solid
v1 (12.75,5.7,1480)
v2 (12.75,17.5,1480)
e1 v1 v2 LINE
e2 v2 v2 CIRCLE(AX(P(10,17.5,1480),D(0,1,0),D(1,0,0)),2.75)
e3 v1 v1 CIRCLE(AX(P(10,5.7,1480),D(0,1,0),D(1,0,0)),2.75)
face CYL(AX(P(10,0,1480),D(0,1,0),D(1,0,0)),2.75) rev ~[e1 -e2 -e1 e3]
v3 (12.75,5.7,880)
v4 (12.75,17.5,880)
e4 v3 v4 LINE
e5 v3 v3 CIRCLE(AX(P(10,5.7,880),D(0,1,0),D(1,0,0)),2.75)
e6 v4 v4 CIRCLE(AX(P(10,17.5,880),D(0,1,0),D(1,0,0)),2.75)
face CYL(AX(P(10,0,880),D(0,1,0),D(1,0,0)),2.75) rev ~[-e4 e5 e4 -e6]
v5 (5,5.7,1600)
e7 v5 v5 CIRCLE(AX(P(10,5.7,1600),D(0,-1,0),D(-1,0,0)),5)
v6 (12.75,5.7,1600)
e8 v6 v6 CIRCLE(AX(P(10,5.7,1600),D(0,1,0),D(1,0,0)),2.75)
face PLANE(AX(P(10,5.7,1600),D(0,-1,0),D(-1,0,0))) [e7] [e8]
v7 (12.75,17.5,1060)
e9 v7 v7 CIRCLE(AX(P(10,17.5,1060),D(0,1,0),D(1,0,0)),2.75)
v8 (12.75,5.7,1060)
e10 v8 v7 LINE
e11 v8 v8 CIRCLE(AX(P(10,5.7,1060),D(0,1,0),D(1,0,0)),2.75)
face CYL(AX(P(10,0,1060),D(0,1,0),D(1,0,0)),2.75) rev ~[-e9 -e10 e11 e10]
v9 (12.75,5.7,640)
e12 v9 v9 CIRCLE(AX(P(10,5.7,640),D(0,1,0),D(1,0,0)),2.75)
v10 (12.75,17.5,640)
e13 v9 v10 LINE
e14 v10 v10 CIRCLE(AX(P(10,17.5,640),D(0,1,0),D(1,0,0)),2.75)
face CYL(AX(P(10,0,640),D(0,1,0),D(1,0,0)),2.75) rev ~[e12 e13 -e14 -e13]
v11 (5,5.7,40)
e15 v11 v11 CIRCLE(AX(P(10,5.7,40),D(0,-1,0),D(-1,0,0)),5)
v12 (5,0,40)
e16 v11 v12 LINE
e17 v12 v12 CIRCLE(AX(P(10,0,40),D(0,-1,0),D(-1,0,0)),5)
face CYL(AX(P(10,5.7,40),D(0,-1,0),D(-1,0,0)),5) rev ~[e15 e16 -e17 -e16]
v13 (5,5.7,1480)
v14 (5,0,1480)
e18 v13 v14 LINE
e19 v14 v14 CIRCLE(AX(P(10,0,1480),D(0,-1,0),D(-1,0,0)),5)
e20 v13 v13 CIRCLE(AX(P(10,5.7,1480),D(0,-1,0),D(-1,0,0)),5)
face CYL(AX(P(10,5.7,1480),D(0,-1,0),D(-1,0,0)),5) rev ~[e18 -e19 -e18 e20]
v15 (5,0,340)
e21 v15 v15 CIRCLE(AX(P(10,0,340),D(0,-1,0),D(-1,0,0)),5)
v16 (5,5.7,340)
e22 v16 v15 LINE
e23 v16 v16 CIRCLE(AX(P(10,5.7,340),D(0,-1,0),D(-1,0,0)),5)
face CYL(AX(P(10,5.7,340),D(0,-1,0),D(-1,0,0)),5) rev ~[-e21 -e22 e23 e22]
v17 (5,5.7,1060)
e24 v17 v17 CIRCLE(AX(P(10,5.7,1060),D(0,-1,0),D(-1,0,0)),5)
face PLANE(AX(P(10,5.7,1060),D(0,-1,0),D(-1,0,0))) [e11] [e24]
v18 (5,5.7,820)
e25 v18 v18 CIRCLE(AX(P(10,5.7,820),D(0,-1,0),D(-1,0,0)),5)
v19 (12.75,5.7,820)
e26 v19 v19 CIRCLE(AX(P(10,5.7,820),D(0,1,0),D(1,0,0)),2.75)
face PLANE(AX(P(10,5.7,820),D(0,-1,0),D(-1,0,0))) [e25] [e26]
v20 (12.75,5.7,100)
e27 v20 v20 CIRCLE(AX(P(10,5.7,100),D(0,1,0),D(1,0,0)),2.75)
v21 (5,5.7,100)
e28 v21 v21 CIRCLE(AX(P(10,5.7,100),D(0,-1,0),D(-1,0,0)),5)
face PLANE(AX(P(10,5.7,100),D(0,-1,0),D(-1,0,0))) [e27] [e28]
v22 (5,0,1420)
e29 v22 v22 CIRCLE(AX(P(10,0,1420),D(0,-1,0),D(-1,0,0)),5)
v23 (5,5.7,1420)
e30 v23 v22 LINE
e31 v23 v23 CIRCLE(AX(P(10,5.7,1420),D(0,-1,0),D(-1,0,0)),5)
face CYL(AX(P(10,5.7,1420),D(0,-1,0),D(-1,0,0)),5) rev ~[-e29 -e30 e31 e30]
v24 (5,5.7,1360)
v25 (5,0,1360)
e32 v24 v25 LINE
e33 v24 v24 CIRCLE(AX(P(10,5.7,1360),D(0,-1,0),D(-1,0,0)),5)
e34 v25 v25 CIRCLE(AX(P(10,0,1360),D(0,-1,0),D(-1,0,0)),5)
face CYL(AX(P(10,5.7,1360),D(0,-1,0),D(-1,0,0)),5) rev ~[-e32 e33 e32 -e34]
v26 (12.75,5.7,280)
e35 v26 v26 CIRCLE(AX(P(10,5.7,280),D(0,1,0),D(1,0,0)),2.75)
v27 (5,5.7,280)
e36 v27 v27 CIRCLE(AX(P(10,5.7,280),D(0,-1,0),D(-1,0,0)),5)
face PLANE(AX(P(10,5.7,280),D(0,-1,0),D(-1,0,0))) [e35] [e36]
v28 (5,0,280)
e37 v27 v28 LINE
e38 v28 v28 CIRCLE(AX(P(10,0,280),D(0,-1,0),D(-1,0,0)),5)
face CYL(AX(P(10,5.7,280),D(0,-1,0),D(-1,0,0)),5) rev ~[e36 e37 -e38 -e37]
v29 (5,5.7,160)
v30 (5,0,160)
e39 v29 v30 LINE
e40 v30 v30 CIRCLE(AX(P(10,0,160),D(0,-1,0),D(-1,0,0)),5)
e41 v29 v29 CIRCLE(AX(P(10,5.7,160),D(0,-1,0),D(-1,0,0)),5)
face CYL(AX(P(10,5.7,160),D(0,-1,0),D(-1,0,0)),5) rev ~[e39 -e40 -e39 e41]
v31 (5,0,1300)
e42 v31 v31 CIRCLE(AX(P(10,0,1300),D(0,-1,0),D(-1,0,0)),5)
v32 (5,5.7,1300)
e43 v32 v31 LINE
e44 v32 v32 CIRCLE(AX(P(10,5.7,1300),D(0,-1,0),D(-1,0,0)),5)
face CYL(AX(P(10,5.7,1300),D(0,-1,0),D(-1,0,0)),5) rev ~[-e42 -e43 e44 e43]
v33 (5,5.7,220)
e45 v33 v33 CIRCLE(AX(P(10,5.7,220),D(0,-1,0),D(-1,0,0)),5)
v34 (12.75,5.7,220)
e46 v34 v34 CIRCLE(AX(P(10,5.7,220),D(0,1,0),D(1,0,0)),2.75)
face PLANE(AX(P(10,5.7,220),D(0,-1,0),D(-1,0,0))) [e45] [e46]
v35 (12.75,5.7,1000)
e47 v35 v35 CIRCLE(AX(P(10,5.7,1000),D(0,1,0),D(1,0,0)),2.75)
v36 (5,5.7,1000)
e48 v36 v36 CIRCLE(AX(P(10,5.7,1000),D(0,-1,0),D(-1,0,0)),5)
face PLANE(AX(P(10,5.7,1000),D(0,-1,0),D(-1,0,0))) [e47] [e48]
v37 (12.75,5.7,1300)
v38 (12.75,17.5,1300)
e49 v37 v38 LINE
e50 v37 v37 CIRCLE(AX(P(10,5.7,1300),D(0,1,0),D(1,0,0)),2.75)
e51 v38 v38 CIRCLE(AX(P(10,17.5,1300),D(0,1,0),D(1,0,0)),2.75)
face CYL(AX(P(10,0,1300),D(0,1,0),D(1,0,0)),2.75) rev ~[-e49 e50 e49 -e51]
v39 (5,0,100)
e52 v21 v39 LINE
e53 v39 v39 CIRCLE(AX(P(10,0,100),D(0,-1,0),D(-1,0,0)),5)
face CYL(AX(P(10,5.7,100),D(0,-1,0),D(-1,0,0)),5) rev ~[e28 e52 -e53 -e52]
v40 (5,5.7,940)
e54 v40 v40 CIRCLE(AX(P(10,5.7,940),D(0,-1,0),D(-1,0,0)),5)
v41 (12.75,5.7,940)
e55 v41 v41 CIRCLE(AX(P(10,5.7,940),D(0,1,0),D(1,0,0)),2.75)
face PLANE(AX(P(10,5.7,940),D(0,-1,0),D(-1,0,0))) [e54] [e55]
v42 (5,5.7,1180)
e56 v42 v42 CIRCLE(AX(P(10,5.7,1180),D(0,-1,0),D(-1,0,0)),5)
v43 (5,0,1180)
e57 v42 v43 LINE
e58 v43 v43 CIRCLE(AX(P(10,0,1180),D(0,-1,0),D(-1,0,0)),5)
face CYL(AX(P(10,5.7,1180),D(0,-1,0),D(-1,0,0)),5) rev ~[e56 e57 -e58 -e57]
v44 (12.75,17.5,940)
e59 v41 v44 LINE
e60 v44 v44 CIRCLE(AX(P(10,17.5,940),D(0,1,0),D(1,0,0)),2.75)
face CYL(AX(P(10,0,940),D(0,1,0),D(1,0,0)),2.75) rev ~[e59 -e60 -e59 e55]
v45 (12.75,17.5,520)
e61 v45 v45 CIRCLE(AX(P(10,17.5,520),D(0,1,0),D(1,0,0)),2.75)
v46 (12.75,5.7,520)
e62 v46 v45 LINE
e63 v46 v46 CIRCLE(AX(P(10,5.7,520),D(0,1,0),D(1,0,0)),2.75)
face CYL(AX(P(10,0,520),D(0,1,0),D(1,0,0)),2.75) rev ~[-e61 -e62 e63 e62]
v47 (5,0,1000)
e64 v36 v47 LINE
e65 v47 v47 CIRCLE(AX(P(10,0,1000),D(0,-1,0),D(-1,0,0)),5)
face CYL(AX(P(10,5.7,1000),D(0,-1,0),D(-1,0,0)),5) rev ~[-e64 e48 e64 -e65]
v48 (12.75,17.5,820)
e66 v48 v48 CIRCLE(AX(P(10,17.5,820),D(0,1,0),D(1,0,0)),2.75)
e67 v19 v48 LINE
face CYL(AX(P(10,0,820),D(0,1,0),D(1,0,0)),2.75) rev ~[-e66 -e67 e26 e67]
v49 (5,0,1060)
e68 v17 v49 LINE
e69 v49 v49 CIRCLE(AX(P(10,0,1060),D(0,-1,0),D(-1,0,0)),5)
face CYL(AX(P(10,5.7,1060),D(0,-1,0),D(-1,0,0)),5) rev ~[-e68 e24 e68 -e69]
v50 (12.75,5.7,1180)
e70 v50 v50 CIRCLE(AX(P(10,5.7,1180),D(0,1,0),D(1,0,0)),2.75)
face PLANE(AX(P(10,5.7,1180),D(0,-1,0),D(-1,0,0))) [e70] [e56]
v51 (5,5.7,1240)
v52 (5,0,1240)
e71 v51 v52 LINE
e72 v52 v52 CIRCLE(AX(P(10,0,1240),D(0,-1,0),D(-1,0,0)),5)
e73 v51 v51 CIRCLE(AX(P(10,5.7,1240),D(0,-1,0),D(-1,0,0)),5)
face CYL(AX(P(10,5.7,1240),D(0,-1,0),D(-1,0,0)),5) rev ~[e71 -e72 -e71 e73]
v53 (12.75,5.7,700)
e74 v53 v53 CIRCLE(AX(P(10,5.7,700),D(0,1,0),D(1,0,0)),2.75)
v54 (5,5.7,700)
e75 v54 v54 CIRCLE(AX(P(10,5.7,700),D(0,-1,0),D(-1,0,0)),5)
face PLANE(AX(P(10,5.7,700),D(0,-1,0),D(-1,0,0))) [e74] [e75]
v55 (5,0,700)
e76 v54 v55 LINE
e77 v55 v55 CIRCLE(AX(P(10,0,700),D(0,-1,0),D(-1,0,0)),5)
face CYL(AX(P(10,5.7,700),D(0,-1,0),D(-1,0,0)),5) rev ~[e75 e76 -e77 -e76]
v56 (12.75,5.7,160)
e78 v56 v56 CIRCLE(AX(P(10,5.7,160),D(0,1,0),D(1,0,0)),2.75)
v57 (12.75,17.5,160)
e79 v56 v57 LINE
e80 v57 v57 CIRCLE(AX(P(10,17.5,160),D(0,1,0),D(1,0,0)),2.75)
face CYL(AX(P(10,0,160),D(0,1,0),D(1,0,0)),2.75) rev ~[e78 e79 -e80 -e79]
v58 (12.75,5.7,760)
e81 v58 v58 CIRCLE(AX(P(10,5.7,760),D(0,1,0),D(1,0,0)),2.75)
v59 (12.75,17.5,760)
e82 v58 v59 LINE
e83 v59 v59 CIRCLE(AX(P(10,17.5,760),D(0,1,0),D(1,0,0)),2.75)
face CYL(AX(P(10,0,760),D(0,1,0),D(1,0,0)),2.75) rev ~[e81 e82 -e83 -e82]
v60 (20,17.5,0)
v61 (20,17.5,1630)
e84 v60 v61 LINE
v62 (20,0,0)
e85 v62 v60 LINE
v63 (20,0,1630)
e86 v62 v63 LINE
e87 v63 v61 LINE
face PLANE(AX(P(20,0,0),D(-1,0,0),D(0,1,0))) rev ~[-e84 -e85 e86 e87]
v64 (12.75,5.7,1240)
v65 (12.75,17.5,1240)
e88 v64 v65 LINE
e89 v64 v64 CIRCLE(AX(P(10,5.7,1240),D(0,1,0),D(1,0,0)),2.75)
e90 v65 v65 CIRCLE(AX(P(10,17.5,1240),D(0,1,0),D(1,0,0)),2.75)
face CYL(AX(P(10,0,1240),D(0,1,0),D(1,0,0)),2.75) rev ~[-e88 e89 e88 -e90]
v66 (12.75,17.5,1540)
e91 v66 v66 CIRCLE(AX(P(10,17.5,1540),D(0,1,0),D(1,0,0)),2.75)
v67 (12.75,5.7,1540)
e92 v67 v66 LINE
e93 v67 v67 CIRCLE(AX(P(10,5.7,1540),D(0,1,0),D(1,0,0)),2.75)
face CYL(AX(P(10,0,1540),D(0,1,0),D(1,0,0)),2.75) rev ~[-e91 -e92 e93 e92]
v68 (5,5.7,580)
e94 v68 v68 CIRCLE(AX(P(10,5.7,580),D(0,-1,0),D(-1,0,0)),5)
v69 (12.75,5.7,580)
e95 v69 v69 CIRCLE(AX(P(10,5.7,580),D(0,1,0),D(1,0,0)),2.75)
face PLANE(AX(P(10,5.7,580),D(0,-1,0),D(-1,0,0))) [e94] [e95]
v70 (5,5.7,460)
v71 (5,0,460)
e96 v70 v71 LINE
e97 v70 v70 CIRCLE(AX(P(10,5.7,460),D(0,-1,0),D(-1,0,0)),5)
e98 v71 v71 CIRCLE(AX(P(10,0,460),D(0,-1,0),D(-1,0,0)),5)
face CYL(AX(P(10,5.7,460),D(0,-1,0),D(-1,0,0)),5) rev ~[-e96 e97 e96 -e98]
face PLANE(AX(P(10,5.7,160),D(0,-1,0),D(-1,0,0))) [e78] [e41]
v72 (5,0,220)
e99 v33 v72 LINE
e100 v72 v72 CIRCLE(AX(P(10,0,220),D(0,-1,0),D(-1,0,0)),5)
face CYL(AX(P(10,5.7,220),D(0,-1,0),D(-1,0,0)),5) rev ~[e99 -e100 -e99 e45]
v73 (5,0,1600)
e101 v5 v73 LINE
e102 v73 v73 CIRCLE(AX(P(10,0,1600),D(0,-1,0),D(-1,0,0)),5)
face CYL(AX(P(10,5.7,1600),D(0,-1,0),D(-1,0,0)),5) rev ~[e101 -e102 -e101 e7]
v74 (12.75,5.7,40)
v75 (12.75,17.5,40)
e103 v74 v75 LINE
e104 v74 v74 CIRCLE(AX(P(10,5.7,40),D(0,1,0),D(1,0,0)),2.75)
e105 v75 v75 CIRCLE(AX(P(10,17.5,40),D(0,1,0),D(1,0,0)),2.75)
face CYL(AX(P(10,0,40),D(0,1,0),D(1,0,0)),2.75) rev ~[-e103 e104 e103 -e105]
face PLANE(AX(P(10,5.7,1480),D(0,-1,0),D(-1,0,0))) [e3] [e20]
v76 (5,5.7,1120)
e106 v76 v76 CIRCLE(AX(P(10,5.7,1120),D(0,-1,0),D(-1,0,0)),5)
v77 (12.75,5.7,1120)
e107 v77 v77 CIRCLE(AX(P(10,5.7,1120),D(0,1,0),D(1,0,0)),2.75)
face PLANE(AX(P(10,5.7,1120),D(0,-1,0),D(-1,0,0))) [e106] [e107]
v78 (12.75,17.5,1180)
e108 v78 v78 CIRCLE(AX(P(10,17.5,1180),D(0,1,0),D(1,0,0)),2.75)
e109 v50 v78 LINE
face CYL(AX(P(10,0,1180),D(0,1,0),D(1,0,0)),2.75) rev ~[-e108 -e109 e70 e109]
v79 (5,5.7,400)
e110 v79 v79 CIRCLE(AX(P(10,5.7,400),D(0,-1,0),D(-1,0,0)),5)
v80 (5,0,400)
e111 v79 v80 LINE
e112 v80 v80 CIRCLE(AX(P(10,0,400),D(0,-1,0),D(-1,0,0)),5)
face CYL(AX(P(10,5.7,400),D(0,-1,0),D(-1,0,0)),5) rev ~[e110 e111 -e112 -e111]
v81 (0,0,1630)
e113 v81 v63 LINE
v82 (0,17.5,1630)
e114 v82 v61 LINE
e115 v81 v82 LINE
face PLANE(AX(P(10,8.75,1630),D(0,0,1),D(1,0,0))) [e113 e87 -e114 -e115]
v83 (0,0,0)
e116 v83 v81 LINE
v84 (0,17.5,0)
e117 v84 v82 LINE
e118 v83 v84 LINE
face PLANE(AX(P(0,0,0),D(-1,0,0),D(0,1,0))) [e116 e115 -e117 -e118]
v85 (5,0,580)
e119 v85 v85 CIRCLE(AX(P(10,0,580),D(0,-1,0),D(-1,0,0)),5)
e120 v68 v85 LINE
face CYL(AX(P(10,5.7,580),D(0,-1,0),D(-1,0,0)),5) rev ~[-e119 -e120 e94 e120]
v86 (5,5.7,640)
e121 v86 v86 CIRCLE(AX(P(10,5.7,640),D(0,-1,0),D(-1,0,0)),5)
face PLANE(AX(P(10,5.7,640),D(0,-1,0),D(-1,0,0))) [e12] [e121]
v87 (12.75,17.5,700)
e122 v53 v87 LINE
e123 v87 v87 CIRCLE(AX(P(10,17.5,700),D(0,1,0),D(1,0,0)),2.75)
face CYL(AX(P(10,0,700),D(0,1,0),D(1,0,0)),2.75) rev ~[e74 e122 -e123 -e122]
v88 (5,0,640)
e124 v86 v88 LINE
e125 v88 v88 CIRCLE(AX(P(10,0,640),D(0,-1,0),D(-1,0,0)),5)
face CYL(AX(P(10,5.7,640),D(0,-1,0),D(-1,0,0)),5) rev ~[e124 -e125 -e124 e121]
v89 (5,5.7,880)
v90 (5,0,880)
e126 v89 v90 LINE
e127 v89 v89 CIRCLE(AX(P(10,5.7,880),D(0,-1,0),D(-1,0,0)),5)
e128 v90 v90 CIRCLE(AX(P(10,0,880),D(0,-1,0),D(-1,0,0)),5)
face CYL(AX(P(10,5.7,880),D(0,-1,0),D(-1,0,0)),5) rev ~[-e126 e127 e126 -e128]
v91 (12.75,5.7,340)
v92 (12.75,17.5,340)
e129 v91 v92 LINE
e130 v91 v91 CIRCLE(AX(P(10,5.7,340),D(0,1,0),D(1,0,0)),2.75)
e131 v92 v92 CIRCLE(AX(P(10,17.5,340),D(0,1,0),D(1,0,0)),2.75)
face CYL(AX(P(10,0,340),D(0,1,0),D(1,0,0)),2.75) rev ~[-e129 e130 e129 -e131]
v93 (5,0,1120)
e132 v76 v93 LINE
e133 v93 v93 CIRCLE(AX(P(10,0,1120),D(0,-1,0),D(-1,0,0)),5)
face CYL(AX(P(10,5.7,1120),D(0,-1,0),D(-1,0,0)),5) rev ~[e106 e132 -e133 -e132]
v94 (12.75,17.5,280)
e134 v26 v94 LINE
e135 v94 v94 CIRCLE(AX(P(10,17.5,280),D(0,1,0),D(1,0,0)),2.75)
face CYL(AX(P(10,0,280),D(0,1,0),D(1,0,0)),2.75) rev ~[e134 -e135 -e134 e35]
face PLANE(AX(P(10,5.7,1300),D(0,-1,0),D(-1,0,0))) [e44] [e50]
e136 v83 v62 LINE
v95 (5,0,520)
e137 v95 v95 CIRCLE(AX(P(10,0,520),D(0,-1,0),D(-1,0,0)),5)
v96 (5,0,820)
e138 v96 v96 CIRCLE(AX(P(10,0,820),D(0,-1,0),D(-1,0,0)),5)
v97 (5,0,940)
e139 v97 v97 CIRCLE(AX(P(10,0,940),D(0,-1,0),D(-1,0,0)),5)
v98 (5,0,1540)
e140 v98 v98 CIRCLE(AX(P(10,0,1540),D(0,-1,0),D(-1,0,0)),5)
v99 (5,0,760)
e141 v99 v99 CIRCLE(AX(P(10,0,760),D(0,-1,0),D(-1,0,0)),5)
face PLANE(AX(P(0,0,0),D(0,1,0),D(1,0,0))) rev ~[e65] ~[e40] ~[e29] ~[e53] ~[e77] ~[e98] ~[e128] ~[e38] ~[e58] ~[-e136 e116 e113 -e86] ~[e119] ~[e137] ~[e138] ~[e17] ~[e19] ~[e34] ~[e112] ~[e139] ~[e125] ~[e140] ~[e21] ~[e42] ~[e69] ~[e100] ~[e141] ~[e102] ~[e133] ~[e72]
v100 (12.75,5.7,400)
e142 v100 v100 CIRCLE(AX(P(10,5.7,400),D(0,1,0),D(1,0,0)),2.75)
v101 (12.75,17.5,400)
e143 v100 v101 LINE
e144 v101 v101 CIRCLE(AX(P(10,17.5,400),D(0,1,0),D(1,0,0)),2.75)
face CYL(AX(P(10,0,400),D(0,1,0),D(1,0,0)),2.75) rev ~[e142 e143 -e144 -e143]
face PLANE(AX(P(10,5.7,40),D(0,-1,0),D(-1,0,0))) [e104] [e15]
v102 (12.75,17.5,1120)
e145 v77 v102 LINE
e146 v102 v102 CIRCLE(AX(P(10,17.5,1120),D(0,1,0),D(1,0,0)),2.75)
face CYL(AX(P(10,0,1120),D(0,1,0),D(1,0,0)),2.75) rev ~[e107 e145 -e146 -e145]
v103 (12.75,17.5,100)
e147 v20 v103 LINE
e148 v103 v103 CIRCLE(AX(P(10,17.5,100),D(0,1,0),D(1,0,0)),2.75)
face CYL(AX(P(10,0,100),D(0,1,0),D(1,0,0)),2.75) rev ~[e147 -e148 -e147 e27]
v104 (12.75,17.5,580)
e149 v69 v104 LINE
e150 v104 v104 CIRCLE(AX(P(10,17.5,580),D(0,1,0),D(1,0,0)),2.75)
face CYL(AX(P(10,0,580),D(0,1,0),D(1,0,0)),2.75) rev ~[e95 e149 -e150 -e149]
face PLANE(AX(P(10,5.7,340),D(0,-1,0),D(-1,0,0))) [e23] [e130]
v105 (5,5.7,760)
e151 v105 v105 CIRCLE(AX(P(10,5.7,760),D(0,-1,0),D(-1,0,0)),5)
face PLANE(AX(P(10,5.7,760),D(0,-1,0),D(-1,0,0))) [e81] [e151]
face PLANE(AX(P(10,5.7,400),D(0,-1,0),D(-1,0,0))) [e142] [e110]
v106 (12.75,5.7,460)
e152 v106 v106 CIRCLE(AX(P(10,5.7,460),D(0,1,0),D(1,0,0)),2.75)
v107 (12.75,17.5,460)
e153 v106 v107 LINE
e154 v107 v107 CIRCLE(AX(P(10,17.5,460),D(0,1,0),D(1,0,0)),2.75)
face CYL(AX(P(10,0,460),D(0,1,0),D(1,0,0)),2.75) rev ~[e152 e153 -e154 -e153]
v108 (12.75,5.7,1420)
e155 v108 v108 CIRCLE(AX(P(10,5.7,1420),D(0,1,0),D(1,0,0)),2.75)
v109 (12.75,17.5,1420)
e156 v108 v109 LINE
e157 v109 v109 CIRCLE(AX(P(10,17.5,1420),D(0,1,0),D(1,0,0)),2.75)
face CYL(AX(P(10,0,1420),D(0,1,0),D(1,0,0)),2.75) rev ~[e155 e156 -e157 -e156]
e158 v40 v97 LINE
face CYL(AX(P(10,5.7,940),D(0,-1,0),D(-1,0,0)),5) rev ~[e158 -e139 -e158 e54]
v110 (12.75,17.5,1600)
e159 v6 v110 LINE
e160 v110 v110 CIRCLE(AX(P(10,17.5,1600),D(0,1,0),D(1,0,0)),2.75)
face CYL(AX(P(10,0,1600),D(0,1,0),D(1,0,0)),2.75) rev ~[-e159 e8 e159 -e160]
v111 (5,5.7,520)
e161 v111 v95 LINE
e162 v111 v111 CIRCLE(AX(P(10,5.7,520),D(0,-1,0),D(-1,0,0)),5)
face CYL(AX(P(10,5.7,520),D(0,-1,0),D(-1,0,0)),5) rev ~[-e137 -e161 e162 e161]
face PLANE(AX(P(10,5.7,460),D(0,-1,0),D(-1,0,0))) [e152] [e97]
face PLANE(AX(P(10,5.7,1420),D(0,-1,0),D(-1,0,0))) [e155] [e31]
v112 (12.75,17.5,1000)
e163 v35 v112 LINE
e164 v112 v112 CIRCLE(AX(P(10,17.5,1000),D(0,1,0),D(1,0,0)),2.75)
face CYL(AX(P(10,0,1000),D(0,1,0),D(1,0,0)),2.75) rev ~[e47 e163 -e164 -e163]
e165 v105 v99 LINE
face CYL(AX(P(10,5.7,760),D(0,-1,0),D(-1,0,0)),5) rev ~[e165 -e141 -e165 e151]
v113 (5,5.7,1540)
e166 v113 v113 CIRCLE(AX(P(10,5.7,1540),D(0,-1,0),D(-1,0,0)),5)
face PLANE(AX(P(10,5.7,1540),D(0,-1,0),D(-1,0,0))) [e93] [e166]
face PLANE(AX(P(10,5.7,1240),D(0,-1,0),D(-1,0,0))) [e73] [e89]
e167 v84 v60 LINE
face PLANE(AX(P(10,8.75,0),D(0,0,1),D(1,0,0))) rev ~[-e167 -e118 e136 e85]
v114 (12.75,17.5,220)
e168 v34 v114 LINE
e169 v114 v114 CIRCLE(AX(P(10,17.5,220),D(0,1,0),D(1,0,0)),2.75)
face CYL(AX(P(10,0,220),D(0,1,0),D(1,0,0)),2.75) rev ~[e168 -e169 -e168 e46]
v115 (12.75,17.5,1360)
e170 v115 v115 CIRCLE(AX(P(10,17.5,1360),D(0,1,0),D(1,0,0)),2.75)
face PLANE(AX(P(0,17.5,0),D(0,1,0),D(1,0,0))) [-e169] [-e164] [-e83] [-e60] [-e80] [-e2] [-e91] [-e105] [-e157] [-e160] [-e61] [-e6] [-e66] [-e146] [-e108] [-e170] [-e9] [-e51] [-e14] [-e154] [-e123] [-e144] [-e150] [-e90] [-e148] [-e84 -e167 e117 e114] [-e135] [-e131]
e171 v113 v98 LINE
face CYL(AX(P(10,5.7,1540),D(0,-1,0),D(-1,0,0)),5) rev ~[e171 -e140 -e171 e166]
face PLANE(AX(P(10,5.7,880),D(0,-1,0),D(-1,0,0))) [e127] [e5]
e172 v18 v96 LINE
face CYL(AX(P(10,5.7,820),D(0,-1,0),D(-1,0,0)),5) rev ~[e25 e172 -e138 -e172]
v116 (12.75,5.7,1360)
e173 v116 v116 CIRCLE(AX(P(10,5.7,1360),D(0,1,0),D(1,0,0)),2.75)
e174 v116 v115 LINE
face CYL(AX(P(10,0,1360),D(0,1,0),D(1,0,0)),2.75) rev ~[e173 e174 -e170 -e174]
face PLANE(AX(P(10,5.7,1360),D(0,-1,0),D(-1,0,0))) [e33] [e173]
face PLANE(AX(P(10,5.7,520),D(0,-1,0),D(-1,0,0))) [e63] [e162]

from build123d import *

# Parameters (mm, degrees)
SKETCH_1_W                = 20
SKETCH_1_H                = 17.5
EXTRUDE_1_DEPTH           = 1630
HOLE_WIZARD_1_D           = 5.5
HOLE_WIZARD_1_CBORE_D     = 10
HOLE_WIZARD_1_CBORE_DEPTH = 5.7
PATTERN_LINEAR_1_COUNT    = 27
PATTERN_LINEAR_1_PITCH    = 60


with BuildPart() as part:
    # 草图1 → 凸台-拉伸1 (new body)
    with BuildSketch(Plane.XY):
        with Locations((10, 8.75)):
            Rectangle(SKETCH_1_W, SKETCH_1_H)
    extrude(amount=EXTRUDE_1_DEPTH)

    # 打孔尺寸(%根据)内六角圆柱头螺钉的类型1 (through all)
    with Locations(Plane(origin=(0, 0, 0), x_dir=(-1, 0, 0), z_dir=(0, -1, 0))):
        with Locations((-10, -1600)):
            hole_wizard_1 = CounterBoreHole(HOLE_WIZARD_1_D / 2, HOLE_WIZARD_1_CBORE_D / 2, HOLE_WIZARD_1_CBORE_DEPTH)

    # 阵列(线性)1: 打孔尺寸(%根据)内六角圆柱头螺钉的类型1 ×27
    with Locations(*[(0, 0, -i * PATTERN_LINEAR_1_PITCH) for i in range(1, PATTERN_LINEAR_1_COUNT)]):
        add(hole_wizard_1, mode=Mode.SUBTRACT)


solid = part.part
